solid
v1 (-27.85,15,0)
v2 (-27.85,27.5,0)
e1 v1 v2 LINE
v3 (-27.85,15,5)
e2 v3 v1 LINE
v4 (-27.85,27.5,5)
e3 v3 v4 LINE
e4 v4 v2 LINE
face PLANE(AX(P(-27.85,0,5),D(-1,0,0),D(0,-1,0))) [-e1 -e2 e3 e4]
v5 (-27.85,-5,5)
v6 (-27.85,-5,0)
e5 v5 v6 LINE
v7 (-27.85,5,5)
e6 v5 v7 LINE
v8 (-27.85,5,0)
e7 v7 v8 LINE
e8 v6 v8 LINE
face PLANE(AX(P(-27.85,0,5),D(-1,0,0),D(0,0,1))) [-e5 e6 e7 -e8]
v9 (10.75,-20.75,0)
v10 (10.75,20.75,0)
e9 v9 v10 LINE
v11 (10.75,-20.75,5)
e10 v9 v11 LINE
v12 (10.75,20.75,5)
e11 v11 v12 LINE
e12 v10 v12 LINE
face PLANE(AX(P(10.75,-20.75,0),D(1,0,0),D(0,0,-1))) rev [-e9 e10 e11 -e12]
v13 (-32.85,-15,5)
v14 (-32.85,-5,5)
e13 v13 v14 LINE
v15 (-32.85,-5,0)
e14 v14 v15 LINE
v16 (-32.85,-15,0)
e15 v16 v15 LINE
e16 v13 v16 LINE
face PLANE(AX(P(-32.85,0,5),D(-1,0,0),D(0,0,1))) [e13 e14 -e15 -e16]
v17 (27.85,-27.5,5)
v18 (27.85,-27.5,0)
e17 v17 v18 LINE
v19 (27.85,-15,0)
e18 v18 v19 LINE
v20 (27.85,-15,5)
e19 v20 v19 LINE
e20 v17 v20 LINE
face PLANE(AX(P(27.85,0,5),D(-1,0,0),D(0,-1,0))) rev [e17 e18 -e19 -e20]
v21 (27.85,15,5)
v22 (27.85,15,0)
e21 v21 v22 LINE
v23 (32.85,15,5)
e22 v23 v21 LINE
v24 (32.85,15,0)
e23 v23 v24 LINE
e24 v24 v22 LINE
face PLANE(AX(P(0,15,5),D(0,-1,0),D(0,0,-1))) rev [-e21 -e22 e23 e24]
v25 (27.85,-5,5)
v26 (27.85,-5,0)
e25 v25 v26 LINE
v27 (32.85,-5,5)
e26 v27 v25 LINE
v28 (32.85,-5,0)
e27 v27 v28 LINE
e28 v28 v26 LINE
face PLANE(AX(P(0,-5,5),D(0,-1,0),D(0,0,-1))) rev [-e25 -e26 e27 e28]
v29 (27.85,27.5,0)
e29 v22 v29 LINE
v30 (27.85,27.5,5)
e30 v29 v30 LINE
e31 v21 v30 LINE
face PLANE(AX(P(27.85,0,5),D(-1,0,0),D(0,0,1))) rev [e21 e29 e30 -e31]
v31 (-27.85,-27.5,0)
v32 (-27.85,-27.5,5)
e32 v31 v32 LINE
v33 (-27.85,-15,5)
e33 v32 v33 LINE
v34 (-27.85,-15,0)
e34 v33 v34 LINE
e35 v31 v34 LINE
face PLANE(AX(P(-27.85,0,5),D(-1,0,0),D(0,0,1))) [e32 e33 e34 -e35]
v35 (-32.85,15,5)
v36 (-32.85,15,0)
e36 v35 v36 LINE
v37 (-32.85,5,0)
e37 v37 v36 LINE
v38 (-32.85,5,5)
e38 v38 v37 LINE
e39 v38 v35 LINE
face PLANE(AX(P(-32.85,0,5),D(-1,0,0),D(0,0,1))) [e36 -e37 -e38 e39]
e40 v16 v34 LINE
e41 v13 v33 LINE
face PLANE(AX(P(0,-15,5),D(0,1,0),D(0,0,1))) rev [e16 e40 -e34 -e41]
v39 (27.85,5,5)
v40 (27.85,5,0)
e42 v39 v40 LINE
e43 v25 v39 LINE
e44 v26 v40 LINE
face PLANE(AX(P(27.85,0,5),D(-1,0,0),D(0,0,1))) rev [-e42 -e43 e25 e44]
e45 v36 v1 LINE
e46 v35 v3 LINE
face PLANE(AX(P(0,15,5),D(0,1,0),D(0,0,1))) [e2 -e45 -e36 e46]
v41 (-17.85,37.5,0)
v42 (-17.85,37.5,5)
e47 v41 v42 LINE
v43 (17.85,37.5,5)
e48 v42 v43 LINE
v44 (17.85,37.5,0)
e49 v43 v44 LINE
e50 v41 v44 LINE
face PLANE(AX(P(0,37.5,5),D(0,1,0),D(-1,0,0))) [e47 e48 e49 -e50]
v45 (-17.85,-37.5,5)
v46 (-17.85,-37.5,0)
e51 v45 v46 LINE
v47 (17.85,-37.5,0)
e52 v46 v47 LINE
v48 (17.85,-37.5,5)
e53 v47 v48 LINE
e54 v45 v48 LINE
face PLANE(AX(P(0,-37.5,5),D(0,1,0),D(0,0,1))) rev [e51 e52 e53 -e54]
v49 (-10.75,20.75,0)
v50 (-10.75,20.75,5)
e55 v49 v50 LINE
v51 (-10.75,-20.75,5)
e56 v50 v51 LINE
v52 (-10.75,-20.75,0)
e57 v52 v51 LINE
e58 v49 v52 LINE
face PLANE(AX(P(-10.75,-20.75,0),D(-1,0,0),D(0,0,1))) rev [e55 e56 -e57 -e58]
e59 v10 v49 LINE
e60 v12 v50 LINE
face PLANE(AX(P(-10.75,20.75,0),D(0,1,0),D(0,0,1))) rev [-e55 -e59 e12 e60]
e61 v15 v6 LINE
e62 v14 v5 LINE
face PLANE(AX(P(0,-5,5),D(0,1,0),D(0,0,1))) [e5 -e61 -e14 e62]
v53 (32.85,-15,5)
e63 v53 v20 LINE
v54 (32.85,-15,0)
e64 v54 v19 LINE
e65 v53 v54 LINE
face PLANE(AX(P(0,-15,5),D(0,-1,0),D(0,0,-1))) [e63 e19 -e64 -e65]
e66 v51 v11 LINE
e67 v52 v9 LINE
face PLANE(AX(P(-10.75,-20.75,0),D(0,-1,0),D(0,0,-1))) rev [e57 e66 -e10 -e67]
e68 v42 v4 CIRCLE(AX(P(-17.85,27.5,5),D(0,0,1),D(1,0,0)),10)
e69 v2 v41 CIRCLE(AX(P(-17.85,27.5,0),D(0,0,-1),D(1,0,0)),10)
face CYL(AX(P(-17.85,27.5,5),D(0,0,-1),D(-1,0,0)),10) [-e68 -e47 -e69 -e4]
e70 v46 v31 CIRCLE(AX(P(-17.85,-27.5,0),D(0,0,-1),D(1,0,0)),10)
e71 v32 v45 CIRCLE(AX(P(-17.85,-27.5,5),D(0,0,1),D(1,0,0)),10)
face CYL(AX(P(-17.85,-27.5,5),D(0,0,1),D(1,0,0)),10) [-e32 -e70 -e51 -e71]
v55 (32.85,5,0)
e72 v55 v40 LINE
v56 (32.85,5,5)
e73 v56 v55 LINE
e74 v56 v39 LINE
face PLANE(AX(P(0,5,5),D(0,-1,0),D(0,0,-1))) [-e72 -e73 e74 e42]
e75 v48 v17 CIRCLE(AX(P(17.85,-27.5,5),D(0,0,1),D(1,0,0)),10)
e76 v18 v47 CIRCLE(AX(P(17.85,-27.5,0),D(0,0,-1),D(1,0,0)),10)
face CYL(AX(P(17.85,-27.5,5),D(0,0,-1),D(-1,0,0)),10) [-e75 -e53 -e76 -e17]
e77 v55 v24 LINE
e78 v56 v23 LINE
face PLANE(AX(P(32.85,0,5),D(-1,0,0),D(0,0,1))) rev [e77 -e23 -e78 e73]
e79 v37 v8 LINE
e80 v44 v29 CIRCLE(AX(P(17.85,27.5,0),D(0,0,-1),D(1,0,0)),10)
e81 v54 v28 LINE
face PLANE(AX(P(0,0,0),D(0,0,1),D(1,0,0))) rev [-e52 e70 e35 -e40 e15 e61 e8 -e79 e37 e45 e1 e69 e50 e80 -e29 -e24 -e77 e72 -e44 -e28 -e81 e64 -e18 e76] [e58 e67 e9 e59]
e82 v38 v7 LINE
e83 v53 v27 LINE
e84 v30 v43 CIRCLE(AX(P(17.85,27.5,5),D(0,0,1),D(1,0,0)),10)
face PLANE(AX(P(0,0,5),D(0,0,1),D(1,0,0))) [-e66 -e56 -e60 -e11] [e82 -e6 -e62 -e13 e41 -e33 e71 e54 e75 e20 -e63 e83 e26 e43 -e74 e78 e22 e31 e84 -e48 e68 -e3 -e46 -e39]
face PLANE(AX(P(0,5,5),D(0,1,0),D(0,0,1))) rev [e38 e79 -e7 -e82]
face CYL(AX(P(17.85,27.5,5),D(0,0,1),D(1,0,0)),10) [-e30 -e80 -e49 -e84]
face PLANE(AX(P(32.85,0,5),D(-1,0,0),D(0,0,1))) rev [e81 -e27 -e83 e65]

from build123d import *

# Parameters (mm, degrees)
EXTRUDE_1_DEPTH     = 5
SKETCH_2_W          = 21.5
SKETCH_2_H          = 41.5
CUT_EXTRUDE_1_DEPTH = 5
FILLET_1_R          = 10


with BuildPart() as part:
    # 草图1 → 凸台-拉伸1 (new body)
    with BuildSketch(Plane.XY):
        Polygon((-27.85, 37.5), (-27.85, 15), (-32.85, 15), (-32.85, 5), (-27.85, 5), (-27.85, -5), (-32.85, -5), (-32.85, -15), (-27.85, -15), (-27.85, -37.5), (27.85, -37.5), (27.85, -15), (32.85, -15), (32.85, -5), (27.85, -5), (27.85, 5), (32.85, 5), (32.85, 15), (27.85, 15), (27.85, 37.5), align=None)
    extrude(amount=EXTRUDE_1_DEPTH)

    # 草图2 → 切除-拉伸1 (cut)
    with BuildSketch(Plane.XY.offset(5)):
        Rectangle(SKETCH_2_W, SKETCH_2_H)
    extrude(amount=-CUT_EXTRUDE_1_DEPTH, mode=Mode.SUBTRACT)

    # 圆角1
    fillet_1_edges = [part.edges().sort_by_distance(p)[0] for p in [
        (27.85, -37.5, 2.5),
        (-27.85, -37.5, 2.5),
        (-27.85, 37.5, 2.5),
        (27.85, 37.5, 2.5),
    ]]
    fillet(fillet_1_edges, radius=FILLET_1_R)


solid = part.part
